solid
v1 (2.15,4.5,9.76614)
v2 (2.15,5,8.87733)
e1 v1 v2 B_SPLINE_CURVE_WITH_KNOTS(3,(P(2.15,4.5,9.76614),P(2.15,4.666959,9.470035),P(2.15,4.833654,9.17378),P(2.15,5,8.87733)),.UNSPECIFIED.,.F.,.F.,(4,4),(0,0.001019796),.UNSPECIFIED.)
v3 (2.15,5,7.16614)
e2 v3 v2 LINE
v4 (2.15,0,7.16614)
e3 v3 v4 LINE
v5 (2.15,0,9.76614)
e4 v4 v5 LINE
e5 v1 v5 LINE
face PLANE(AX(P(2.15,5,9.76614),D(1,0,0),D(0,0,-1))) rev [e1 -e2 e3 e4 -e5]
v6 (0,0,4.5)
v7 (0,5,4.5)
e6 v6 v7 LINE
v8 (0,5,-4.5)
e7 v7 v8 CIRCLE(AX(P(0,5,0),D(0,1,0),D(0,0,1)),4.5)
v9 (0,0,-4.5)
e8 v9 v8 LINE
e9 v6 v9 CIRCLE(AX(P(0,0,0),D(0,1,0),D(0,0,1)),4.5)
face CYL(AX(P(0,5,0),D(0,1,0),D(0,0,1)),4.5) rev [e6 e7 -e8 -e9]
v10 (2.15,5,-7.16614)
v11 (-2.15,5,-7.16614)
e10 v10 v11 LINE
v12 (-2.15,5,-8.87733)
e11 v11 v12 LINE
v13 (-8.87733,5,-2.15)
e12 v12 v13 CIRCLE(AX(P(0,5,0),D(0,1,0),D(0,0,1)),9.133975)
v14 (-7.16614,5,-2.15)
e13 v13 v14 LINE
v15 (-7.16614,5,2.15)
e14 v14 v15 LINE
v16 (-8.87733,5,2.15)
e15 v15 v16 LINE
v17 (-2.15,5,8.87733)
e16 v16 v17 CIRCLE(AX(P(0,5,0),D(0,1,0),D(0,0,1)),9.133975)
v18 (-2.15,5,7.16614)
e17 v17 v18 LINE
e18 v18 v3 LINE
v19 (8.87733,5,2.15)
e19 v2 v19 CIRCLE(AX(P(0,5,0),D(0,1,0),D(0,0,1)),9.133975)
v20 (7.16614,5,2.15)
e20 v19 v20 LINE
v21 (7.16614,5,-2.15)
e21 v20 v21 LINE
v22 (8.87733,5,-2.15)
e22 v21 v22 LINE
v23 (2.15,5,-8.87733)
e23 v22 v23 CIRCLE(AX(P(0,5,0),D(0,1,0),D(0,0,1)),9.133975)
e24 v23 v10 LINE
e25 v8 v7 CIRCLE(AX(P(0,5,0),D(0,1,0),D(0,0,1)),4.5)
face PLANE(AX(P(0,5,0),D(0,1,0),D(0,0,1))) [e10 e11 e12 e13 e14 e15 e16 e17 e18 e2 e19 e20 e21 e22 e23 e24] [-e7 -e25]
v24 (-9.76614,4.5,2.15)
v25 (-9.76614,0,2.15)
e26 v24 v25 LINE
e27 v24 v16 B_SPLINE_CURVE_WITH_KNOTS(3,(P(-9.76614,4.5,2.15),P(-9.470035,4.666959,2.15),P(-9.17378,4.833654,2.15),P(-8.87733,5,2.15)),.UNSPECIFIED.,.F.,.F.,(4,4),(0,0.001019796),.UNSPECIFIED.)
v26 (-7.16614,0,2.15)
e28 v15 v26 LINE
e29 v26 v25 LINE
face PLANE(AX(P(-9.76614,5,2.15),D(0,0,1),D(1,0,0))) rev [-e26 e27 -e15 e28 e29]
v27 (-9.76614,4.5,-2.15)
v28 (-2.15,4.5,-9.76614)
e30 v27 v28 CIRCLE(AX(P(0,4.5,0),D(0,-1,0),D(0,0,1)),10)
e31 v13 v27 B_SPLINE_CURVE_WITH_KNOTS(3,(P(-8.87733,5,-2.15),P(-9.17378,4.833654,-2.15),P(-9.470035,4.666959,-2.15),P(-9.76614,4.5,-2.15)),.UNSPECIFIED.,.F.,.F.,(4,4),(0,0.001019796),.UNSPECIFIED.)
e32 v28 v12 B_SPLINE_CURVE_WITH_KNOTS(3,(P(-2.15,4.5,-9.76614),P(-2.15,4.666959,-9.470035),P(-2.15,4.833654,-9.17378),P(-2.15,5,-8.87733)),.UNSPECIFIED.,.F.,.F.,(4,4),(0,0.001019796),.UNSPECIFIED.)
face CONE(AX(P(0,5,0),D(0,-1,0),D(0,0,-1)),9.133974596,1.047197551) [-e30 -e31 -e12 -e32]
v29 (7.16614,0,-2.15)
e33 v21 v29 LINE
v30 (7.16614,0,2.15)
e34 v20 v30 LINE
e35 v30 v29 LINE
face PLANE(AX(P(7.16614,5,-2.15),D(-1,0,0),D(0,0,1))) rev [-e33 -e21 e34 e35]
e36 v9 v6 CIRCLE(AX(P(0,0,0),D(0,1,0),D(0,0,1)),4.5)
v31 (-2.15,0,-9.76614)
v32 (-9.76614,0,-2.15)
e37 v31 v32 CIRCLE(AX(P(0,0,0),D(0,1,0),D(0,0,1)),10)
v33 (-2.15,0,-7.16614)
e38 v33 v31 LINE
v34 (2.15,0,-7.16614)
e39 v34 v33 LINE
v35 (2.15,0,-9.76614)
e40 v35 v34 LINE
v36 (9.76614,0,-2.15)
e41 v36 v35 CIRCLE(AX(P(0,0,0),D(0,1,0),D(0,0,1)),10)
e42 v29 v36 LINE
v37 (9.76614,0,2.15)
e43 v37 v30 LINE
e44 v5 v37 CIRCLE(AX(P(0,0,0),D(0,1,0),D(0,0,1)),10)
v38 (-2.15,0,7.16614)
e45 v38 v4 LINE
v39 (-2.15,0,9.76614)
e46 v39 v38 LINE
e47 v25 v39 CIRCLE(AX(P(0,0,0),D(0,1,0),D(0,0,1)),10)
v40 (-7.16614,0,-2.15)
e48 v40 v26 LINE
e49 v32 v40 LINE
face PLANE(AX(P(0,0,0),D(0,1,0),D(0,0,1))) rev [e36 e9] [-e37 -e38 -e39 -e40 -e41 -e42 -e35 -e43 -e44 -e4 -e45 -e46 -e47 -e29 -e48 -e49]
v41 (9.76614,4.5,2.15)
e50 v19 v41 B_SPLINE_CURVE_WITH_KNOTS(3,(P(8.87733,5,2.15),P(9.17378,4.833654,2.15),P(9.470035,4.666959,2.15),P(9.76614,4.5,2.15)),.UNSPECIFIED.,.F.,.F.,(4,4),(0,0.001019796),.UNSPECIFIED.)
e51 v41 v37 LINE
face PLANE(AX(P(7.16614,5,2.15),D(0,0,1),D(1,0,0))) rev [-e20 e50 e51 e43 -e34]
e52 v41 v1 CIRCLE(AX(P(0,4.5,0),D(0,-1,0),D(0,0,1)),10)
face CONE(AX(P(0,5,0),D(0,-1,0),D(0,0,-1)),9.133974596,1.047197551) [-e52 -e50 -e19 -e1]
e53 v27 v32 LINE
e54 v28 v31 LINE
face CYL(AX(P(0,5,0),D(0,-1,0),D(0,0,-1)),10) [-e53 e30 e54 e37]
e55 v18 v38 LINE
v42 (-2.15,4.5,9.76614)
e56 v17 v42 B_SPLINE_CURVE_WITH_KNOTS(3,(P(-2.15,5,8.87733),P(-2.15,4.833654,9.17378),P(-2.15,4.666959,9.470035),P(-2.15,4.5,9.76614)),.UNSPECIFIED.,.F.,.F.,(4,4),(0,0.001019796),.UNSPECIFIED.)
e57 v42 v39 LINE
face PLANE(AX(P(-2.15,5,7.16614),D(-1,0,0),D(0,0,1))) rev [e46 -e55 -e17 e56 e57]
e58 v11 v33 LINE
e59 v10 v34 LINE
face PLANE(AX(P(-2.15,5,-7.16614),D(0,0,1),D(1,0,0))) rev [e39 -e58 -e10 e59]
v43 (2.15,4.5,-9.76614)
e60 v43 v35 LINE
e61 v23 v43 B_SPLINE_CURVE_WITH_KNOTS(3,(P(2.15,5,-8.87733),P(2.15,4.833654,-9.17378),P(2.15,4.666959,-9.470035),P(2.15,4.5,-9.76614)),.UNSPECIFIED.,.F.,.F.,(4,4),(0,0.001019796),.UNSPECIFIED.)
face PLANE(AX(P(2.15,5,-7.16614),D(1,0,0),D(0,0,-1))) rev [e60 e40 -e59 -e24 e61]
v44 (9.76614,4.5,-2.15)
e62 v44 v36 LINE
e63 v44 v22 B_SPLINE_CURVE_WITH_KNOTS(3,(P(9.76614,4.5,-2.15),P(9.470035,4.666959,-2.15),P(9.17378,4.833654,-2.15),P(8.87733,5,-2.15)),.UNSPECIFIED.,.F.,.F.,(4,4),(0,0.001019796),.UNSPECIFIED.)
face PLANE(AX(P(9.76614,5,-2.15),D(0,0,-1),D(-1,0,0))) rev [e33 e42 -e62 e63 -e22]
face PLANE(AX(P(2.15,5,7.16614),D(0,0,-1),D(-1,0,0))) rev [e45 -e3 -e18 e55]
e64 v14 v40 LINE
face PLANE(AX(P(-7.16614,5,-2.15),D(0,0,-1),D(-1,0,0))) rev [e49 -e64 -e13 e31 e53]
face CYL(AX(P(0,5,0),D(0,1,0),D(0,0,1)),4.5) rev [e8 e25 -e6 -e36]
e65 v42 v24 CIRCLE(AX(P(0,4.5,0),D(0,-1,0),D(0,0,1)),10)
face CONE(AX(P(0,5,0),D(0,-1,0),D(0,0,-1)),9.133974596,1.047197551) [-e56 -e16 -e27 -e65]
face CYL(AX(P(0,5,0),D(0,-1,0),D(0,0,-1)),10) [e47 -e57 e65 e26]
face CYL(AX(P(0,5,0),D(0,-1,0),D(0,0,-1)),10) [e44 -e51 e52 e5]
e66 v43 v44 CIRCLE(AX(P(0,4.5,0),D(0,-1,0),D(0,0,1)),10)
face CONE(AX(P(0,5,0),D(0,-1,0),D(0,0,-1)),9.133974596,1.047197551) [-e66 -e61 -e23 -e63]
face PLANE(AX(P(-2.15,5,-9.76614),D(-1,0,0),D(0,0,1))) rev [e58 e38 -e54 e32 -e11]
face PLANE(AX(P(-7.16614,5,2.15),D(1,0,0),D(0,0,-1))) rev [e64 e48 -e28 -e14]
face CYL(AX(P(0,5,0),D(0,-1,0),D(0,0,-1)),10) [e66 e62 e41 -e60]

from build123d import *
from OCP.BRepFilletAPI import BRepFilletAPI_MakeChamfer

# Parameters (mm, degrees)
EXTRUDE_1_DEPTH = 5
M10X1_0_1_D     = 9
CHAMFER_1_SIZE  = 0.5
CHAMFER_1_SIZE2 = 0.866025404


with BuildPart() as part:
    # 草图1 → 凸台-拉伸1 (new body)
    with BuildSketch(Plane(origin=(0, 0, 0), x_dir=(1, 0, 0), z_dir=(0, 1, 0))):
        with BuildLine():
            Line((-2.15, 9.766140486), (-2.15, 7.166140486))
            Line((-2.15, 7.166140486), (2.15, 7.166140486))
            Line((2.15, 7.166140486), (2.15, 9.766140486))
            ThreePointArc((2.15, 9.766140486), (7.071067812, 7.071067812), (9.766140486, 2.15))
            Line((9.766140486, 2.15), (7.166140486, 2.15))
            Line((7.166140486, 2.15), (7.166140486, -2.15))
            Line((7.166140486, -2.15), (9.766140486, -2.15))
            ThreePointArc((9.766140486, -2.15), (7.071067812, -7.071067812), (2.15, -9.766140486))
            Line((2.15, -9.766140486), (2.15, -7.166140486))
            Line((2.15, -7.166140486), (-2.15, -7.166140486))
            Line((-2.15, -7.166140486), (-2.15, -9.766140486))
            ThreePointArc((-2.15, -9.766140486), (-7.071067812, -7.071067812), (-9.766140486, -2.15))
            Line((-9.766140486, -2.15), (-7.166140486, -2.15))
            Line((-7.166140486, -2.15), (-7.166140486, 2.15))
            Line((-7.166140486, 2.15), (-9.766140486, 2.15))
            ThreePointArc((-9.766140486, 2.15), (-7.071067812, 7.071067812), (-2.15, 9.766140486))
        make_face()
    extrude(amount=EXTRUDE_1_DEPTH)

    # M10x1.0 螺纹孔1 (through all)
    with Locations(Plane(origin=(0, 5, 0), x_dir=(1, 0, 0), z_dir=(0, 1, 0))):
        with Locations((0, 0)):
            Hole(M10X1_0_1_D / 2)

    # 倒角1: one chamfer whose edges measure the first distance from different faces: ONE call of the kernel's chamfer builder (chamfer() names one face for all edges)
    chamfer_1_edges_1 = [part.edges().sort_by_distance(p)[0] for p in [
        (-7.071067812, 5, 7.071067812),
    ]]
    chamfer_1_side_1 = [part.faces().sort_by_distance(p)[0] for p in [
        (-7.071067812, 2.5, 7.071067812),
    ]]
    chamfer_1_edges_2 = [part.edges().sort_by_distance(p)[0] for p in [
        (7.071067812, 5, 7.071067812),
    ]]
    chamfer_1_side_2 = [part.faces().sort_by_distance(p)[0] for p in [
        (7.071067812, 2.5, 7.071067812),
    ]]
    chamfer_1_edges_3 = [part.edges().sort_by_distance(p)[0] for p in [
        (-7.071067812, 5, -7.071067812),
    ]]
    chamfer_1_side_3 = [part.faces().sort_by_distance(p)[0] for p in [
        (-7.071067812, 2.5, -7.071067812),
    ]]
    chamfer_1_edges_4 = [part.edges().sort_by_distance(p)[0] for p in [
        (7.071067812, 5, -7.071067812),
    ]]
    chamfer_1_side_4 = [part.faces().sort_by_distance(p)[0] for p in [
        (7.071067812, 2.5, -7.071067812),
    ]]
    chamfer_1 = BRepFilletAPI_MakeChamfer(part.part.solid().wrapped)
    for e in chamfer_1_edges_1:
        chamfer_1.Add(CHAMFER_1_SIZE, CHAMFER_1_SIZE2, e.wrapped, chamfer_1_side_1[0].wrapped)  # the first distance lies on this face
    for e in chamfer_1_edges_2:
        chamfer_1.Add(CHAMFER_1_SIZE, CHAMFER_1_SIZE2, e.wrapped, chamfer_1_side_2[0].wrapped)  # the first distance lies on this face
    for e in chamfer_1_edges_3:
        chamfer_1.Add(CHAMFER_1_SIZE, CHAMFER_1_SIZE2, e.wrapped, chamfer_1_side_3[0].wrapped)  # the first distance lies on this face
    for e in chamfer_1_edges_4:
        chamfer_1.Add(CHAMFER_1_SIZE, CHAMFER_1_SIZE2, e.wrapped, chamfer_1_side_4[0].wrapped)  # the first distance lies on this face
    add(Compound.cast(chamfer_1.Shape()), mode=Mode.REPLACE)


solid = part.part
